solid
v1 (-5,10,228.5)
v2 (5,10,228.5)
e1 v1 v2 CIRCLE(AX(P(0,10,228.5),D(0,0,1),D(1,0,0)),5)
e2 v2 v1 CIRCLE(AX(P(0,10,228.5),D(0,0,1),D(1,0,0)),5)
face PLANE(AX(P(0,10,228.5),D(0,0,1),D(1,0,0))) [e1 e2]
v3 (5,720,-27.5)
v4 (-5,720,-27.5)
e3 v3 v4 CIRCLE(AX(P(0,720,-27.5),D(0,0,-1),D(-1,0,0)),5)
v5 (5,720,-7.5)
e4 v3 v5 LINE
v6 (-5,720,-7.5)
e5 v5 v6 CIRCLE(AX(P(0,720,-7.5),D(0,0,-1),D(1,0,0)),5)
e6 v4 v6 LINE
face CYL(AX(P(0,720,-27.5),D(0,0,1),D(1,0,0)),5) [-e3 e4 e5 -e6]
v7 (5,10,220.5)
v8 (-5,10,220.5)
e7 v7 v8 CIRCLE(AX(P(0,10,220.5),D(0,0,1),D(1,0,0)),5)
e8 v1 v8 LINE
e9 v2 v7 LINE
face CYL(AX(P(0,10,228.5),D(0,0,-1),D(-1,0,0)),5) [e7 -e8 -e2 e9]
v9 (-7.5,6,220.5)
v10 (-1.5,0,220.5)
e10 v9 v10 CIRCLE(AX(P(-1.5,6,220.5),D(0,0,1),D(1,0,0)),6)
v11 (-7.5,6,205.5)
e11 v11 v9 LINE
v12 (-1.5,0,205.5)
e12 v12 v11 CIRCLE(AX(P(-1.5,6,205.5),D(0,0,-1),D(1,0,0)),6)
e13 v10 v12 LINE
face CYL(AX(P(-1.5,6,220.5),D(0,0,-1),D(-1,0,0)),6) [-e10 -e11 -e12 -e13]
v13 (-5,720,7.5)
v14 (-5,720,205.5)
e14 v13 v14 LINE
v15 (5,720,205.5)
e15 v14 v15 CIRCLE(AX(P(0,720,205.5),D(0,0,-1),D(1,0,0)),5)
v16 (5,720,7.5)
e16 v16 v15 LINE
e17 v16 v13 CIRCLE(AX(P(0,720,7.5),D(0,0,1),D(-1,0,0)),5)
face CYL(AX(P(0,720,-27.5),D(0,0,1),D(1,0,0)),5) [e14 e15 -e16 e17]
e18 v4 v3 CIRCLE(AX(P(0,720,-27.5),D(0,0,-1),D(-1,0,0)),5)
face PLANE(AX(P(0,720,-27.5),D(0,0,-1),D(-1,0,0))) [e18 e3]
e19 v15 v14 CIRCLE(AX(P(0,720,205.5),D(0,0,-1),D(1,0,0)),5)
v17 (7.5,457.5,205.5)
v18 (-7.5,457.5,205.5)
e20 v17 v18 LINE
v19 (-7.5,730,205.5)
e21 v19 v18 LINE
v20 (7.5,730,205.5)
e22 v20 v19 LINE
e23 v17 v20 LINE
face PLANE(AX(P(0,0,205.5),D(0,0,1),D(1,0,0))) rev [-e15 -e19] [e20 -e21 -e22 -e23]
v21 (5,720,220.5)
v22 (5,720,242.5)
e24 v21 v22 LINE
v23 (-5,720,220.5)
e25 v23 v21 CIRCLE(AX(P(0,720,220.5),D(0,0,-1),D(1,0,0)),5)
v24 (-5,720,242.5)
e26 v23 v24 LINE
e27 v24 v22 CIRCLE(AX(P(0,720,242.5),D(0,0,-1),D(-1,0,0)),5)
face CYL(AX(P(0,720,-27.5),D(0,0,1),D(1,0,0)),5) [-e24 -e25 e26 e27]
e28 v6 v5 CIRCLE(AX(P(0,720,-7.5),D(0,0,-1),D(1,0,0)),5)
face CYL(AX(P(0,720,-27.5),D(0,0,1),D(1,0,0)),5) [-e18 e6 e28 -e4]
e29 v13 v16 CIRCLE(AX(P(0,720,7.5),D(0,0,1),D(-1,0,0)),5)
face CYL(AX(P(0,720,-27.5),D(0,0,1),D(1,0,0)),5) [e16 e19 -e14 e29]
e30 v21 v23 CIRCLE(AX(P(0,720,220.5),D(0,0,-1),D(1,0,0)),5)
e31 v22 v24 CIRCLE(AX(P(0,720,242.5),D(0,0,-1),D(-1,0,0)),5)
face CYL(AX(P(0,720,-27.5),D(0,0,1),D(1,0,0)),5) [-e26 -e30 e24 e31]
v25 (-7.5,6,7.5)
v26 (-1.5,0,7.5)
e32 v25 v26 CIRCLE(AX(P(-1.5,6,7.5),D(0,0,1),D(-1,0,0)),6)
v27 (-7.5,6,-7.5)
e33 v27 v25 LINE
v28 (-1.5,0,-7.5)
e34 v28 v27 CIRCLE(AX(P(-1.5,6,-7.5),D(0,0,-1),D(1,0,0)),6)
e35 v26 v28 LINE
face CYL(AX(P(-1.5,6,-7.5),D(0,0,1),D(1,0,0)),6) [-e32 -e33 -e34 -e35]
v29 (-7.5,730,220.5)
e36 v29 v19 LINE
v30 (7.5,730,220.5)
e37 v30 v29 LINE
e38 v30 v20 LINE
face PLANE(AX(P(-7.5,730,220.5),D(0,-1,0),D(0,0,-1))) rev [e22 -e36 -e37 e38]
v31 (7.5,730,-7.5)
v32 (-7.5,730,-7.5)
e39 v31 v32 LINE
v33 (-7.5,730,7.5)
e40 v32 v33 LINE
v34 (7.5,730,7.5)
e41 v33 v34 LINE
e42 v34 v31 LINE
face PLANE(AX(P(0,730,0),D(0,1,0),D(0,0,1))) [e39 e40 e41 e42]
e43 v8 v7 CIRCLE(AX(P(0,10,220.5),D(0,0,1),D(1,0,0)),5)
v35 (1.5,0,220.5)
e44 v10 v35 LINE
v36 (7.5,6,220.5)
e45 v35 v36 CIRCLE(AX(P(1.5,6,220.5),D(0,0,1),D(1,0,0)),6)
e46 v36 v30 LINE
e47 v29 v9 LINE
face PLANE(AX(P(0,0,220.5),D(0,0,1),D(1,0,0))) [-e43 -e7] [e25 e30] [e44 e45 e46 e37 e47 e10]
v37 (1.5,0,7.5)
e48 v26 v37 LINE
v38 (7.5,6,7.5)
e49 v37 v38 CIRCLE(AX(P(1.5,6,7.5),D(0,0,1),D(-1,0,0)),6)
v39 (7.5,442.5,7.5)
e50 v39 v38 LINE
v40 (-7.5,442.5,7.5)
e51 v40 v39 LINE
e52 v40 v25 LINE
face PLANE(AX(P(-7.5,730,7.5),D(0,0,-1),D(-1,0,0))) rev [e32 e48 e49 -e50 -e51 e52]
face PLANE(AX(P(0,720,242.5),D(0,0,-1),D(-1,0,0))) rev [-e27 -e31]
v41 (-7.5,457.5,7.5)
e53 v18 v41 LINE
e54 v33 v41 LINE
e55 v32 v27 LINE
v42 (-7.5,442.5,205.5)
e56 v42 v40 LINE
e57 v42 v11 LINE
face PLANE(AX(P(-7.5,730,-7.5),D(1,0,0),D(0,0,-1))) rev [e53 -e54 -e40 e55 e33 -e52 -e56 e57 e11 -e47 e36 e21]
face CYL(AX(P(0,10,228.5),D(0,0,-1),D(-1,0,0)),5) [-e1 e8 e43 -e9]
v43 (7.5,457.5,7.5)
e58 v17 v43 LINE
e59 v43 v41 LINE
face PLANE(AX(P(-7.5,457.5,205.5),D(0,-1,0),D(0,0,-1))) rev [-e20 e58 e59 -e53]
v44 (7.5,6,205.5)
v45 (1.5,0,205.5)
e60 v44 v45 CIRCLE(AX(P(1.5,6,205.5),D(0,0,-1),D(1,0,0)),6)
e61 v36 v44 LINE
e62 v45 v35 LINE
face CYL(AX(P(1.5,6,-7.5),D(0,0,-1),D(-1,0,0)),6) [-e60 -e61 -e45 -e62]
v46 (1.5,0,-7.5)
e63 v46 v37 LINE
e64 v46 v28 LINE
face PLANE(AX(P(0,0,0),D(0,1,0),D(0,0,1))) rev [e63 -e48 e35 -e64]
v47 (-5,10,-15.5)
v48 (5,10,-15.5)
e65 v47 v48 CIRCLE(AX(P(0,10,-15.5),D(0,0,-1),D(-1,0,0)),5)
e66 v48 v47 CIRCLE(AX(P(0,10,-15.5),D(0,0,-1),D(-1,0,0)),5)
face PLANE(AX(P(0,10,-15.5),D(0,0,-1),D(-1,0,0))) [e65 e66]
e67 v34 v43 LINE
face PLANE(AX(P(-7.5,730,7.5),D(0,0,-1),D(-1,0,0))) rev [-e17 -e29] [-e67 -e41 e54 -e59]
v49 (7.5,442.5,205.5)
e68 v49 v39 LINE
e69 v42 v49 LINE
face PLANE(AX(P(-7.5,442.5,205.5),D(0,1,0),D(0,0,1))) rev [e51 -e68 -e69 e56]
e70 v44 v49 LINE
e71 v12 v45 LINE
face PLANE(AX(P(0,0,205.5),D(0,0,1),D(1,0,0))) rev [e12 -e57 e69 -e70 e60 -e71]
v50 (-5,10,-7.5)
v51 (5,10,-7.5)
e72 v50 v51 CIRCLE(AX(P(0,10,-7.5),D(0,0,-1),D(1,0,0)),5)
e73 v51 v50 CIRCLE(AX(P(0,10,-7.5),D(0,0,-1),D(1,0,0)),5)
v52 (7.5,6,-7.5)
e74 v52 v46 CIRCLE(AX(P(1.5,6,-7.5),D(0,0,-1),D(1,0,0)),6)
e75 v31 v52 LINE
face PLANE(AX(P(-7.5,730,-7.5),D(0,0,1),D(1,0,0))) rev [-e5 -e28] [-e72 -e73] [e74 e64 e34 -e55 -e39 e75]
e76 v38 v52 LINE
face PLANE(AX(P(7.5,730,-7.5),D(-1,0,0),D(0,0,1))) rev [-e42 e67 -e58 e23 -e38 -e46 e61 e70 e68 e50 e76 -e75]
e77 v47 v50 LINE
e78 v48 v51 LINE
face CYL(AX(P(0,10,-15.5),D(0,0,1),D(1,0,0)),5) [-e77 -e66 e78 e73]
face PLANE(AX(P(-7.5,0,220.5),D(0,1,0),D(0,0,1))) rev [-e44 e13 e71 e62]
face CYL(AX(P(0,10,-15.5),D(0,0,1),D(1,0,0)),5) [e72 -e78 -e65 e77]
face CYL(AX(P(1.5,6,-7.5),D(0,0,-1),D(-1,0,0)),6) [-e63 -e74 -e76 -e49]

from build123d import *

# Parameters (mm, degrees)
SKETCH1_W                = 15
SKETCH1_H                = 15
BOSS_EXTRUDE1_DEPTH      = 730
SKETCH2_R                = 5
BOSS_EXTRUDE2_DEPTH      = 8
SKETCH4_W                = 15
SKETCH4_H                = 15
BOSS_EXTRUDE3_DEPTH      = 198
SKETCH5_W                = 15
SKETCH5_H                = 730
BOSS_EXTRUDE4_DEPTH      = 15
BOSS_EXTRUDE5_START      = 8
SKETCH6_R                = 5
BOSS_EXTRUDE5_DEPTH      = 8
FILLET1_R                = 6
BOSS_EXTRUDE6_DEPTH      = 20
BOSS_EXTRUDE6_DEPTH_BACK = 250
SKETCH7_R                = 5


with BuildPart() as part:
    # Sketch1 → Boss-Extrude1 (new body)
    with BuildSketch(Plane(origin=(0, 0, 0), x_dir=(1, 0, 0), z_dir=(0, 1, 0))):
        Rectangle(SKETCH1_W, SKETCH1_H)
    extrude(amount=BOSS_EXTRUDE1_DEPTH)

    # Sketch2 → Boss-Extrude2 (add)
    with BuildSketch(Plane(origin=(0, 0, -7.5), x_dir=(-1, 0, 0), z_dir=(0, 0, -1))):
        with Locations(Location((0, 10, 0), (0, 0, 180))):
            Circle(SKETCH2_R)
    extrude(amount=BOSS_EXTRUDE2_DEPTH)

    # Sketch4 → Boss-Extrude3 (add)
    with BuildSketch(Plane.XY.offset(7.5)):
        with Locations((0, 450)):
            Rectangle(SKETCH4_W, SKETCH4_H)
    extrude(amount=BOSS_EXTRUDE3_DEPTH)

    # Sketch5 → Boss-Extrude4 (add)
    with BuildSketch(Plane.XY.offset(205.5)):
        with Locations((0, 365)):
            Rectangle(SKETCH5_W, SKETCH5_H)
    extrude(amount=BOSS_EXTRUDE4_DEPTH)

    # Sketch6 → Boss-Extrude5 (add)
    with BuildSketch(Plane.XY.offset(220.5).offset(BOSS_EXTRUDE5_START)):
        with Locations((0, 10)):
            Circle(SKETCH6_R)
    extrude(amount=-BOSS_EXTRUDE5_DEPTH)

    # Fillet1
    fillet1_edges = [part.edges().sort_by_distance(p)[0] for p in [
        (7.5, 0, 213),
        (-7.5, 0, 213),
        (-7.5, 0, 0),
        (7.5, 0, 0),
    ]]
    fillet(fillet1_edges, radius=FILLET1_R)

    # Sketch7 → Boss-Extrude6 (add, two sides: drawn at the far end of the back side and taken through both)
    with BuildSketch(Plane(origin=(0, 0, -7.5), x_dir=(-1, 0, 0), z_dir=(0, 0, -1)).offset(-BOSS_EXTRUDE6_DEPTH_BACK)):
        with Locations(Location((0, 720, 0), (0, 0, 180))):
            Circle(SKETCH7_R)
    extrude(amount=BOSS_EXTRUDE6_DEPTH + BOSS_EXTRUDE6_DEPTH_BACK)


solid = part.part
